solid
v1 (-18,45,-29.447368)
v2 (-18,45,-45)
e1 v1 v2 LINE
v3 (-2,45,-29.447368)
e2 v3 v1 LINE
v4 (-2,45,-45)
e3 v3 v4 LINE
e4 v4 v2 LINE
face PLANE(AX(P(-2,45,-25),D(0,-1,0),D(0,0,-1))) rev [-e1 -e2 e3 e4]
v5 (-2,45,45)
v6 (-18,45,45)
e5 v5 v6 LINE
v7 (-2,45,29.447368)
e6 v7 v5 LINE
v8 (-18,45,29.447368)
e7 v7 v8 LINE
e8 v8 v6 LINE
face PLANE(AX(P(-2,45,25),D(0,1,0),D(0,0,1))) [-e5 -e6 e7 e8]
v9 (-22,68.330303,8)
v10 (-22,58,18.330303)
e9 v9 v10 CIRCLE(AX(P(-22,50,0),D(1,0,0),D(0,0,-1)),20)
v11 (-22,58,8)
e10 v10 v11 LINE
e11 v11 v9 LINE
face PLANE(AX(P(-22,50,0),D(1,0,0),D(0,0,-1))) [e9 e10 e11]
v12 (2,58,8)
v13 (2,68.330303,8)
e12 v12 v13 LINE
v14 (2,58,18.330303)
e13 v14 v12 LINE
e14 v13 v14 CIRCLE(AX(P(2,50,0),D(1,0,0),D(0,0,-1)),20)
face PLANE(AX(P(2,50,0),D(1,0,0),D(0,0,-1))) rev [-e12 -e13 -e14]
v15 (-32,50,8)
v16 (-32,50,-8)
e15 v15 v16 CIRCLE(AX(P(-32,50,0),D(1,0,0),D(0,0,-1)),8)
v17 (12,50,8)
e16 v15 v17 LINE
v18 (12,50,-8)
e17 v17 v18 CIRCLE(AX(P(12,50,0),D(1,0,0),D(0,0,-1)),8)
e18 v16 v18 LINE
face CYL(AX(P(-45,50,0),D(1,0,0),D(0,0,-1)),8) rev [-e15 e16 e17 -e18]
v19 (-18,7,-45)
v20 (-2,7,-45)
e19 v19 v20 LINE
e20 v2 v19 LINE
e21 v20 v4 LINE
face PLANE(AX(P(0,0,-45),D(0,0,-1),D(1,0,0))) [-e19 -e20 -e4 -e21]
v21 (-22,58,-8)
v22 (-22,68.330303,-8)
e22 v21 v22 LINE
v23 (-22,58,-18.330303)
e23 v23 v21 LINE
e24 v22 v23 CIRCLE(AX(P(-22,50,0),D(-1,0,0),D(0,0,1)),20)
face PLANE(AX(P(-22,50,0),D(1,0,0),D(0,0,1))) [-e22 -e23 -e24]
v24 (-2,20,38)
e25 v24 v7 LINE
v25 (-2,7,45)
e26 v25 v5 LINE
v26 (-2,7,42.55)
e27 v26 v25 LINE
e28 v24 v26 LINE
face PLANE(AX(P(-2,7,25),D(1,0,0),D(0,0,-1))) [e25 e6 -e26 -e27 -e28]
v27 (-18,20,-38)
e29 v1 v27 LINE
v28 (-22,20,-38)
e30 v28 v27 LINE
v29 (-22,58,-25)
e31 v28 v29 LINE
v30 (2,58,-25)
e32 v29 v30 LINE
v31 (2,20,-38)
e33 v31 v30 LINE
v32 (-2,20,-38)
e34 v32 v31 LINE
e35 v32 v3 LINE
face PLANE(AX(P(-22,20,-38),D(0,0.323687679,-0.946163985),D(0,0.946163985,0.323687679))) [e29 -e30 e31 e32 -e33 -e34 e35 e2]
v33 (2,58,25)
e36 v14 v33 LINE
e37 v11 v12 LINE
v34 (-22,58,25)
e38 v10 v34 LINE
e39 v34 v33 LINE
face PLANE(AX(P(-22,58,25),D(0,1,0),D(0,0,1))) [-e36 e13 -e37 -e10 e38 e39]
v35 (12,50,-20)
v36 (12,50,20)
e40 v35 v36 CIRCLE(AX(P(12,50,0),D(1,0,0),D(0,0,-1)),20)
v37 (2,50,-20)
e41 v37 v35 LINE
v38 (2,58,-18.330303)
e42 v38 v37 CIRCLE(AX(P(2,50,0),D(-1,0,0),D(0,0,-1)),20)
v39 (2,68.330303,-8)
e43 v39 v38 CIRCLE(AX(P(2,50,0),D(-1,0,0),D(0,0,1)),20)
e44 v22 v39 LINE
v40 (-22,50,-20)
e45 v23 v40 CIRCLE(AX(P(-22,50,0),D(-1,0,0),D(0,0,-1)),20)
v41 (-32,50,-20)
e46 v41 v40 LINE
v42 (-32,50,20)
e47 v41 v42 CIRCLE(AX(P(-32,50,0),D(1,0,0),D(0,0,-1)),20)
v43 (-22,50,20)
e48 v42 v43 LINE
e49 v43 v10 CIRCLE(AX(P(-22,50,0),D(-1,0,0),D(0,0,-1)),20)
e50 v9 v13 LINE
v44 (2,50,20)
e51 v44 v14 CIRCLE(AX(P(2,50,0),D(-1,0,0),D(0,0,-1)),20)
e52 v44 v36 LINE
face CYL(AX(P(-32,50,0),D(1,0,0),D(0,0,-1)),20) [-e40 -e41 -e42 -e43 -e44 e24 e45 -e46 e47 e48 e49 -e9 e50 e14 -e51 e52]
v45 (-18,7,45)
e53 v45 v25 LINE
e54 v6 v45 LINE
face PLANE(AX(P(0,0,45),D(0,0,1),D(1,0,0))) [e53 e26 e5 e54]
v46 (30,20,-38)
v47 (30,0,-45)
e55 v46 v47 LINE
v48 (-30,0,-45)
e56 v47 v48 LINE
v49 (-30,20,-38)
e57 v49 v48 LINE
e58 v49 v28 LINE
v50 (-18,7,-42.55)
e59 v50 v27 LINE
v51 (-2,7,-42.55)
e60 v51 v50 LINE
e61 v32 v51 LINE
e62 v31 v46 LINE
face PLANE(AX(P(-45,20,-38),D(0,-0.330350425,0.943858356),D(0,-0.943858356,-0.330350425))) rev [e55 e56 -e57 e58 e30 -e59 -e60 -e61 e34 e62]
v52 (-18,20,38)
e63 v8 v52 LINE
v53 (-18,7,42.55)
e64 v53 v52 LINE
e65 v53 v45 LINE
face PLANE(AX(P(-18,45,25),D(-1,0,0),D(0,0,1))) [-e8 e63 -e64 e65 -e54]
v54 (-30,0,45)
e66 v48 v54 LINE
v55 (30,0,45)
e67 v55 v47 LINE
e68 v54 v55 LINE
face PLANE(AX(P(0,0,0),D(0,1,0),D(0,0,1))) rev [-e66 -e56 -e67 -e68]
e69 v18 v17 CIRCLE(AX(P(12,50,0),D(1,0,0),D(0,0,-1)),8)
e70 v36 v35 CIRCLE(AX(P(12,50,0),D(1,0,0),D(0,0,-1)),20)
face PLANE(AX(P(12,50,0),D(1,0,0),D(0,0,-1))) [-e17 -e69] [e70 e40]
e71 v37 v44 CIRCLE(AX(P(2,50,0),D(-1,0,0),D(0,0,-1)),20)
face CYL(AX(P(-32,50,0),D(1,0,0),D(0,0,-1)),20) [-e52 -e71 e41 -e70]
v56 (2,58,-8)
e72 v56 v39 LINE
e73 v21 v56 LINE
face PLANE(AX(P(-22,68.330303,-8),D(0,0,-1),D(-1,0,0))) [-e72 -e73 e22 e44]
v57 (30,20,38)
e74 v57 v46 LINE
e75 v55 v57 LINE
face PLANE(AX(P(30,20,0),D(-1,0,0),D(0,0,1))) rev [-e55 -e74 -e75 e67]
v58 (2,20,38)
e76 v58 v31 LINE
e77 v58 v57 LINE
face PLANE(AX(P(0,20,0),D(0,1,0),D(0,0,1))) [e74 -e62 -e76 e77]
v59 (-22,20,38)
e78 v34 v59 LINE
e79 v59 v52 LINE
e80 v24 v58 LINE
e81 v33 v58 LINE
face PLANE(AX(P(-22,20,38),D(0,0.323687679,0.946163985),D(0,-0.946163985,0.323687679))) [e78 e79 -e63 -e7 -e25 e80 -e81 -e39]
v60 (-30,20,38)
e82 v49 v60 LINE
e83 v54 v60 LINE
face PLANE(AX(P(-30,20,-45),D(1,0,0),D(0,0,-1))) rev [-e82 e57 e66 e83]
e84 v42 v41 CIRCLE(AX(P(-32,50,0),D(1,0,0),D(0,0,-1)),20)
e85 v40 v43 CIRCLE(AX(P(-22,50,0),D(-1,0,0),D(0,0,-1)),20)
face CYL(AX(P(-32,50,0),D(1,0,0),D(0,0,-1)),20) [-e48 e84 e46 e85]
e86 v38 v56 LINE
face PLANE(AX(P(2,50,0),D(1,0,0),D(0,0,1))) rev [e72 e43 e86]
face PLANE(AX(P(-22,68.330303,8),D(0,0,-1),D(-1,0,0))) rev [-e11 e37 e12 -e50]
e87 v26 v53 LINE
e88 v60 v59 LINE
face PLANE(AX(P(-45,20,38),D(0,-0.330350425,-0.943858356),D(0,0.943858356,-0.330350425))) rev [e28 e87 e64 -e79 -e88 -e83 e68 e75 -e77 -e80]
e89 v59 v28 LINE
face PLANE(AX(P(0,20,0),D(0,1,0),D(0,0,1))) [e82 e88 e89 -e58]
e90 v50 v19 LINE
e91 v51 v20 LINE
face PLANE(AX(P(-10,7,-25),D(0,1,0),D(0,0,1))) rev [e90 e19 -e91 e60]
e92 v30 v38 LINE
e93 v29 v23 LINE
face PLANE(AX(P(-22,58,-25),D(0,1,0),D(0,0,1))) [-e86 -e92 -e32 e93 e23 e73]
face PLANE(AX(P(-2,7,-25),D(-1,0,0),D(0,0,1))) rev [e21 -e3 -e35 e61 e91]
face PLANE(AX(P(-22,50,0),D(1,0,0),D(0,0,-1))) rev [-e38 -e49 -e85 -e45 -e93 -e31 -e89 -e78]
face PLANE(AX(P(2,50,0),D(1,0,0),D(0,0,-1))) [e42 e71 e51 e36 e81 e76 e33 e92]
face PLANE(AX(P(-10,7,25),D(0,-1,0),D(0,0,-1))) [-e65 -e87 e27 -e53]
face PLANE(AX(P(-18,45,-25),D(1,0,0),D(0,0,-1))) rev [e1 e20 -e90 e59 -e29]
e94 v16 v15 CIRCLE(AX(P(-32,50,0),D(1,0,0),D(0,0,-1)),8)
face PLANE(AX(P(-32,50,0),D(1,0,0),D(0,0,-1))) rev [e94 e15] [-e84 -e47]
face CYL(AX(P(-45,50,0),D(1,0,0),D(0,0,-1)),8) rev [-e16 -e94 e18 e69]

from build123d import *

# Parameters (mm, degrees)
BASE_BLOCK_DEPTH      = 20
BASE_RECESS_CUT_DEPTH = 75
HUB_CIRCLE_SKETCH_R   = 20
BEARING_HUB_DEPTH     = 44
SUPPORT_WEB_DEPTH     = 24
SIDE_WINDOW_CUT_DEPTH = 24
BEARING_BORE_SKETCH_R = 8
BEARING_BORE_DEPTH    = 57
SIDE_RIB_DEPTH        = 20


with BuildPart() as part:
    # Base Profile Sketch → Base Block (new body)
    with BuildSketch(Plane(origin=(0, 0, 0), x_dir=(1, 0, 0), z_dir=(0, 1, 0))):
        Polygon((30, 0), (30, 45), (-30, 45), (-30, -45), (30, -45), align=None)
    extrude(amount=BASE_BLOCK_DEPTH)

    # Base Recess Sketch → Base Recess Cut (cut)
    with BuildSketch(Plane(origin=(30, 0, 0), x_dir=(0, 0, -1), z_dir=(1, 0, 0))):
        Polygon((38, 20), (45, 0), (45, 20), align=None)
        Polygon((-38, 20), (-45, 0), (-45, 20), align=None)
    extrude(amount=-BASE_RECESS_CUT_DEPTH, mode=Mode.SUBTRACT)



with BuildPart() as body_2:
    # Hub Circle Sketch → Bearing Hub (new body)
    with BuildSketch(Plane(origin=(12, 0, 0), x_dir=(0, 0, -1), z_dir=(1, 0, 0))):
        with Locations((0, 50)):
            Circle(HUB_CIRCLE_SKETCH_R)
    extrude(amount=-BEARING_HUB_DEPTH)


with BuildPart() as part_1:
    add(part.part)

    add(body_2.part)  # Support Web merges body 2
    # Support Web Sketch → Support Web (add)
    with BuildSketch(Plane(origin=(2, 0, 0), x_dir=(0, 0, -1), z_dir=(1, 0, 0))):
        with BuildLine():
            Line((25, 20), (-25, 20))
            Line((-25, 20), (-38, 20))
            Line((-38, 20), (-25, 58))
            Line((-25, 58), (-18.33030278, 58))
            ThreePointArc((-18.33030278, 58), (0, 30), (18.33030278, 58))
            Line((18.33030278, 58), (25, 58))
            Line((25, 58), (38, 20))
            Line((38, 20), (25, 20))
        make_face()
    extrude(amount=-SUPPORT_WEB_DEPTH)

    # Side Window Sketch → Side Window Cut (cut)
    with BuildSketch(Plane(origin=(2, 0, 0), x_dir=(0, 0, -1), z_dir=(1, 0, 0))):
        with BuildLine():
            Line((-8, 68.33030278), (-8, 58))
            Line((-8, 58), (-18.33030278, 58))
            ThreePointArc((-18.33030278, 58), (-14.142135624, 64.142135624), (-8, 68.33030278))
        make_face()
    side_window_cut = extrude(amount=-SIDE_WINDOW_CUT_DEPTH, mode=Mode.SUBTRACT)

    # Side Window Mirror: Side Window Cut across plane
    add(side_window_cut.mirror(Plane.XY), mode=Mode.SUBTRACT)

    # Bearing Bore Sketch → Bearing Bore (cut)
    with BuildSketch(Plane(origin=(12, 0, 0), x_dir=(0, 0, -1), z_dir=(1, 0, 0))):
        with Locations((0, 50)):
            Circle(BEARING_BORE_SKETCH_R)
    extrude(amount=-BEARING_BORE_DEPTH, mode=Mode.SUBTRACT)

    # Side Rib Sketch → Side Rib (add)
    with BuildSketch(Plane.XY.offset(45)):
        Polygon((-10, 7), (-2, 7), (-2, 45), (-18, 45), (-18, 7), align=None)
    side_rib = extrude(amount=-SIDE_RIB_DEPTH)

    # Side Rib Mirror: Side Rib across plane
    add(side_rib.mirror(Plane.XY))


solid = part_1.part
